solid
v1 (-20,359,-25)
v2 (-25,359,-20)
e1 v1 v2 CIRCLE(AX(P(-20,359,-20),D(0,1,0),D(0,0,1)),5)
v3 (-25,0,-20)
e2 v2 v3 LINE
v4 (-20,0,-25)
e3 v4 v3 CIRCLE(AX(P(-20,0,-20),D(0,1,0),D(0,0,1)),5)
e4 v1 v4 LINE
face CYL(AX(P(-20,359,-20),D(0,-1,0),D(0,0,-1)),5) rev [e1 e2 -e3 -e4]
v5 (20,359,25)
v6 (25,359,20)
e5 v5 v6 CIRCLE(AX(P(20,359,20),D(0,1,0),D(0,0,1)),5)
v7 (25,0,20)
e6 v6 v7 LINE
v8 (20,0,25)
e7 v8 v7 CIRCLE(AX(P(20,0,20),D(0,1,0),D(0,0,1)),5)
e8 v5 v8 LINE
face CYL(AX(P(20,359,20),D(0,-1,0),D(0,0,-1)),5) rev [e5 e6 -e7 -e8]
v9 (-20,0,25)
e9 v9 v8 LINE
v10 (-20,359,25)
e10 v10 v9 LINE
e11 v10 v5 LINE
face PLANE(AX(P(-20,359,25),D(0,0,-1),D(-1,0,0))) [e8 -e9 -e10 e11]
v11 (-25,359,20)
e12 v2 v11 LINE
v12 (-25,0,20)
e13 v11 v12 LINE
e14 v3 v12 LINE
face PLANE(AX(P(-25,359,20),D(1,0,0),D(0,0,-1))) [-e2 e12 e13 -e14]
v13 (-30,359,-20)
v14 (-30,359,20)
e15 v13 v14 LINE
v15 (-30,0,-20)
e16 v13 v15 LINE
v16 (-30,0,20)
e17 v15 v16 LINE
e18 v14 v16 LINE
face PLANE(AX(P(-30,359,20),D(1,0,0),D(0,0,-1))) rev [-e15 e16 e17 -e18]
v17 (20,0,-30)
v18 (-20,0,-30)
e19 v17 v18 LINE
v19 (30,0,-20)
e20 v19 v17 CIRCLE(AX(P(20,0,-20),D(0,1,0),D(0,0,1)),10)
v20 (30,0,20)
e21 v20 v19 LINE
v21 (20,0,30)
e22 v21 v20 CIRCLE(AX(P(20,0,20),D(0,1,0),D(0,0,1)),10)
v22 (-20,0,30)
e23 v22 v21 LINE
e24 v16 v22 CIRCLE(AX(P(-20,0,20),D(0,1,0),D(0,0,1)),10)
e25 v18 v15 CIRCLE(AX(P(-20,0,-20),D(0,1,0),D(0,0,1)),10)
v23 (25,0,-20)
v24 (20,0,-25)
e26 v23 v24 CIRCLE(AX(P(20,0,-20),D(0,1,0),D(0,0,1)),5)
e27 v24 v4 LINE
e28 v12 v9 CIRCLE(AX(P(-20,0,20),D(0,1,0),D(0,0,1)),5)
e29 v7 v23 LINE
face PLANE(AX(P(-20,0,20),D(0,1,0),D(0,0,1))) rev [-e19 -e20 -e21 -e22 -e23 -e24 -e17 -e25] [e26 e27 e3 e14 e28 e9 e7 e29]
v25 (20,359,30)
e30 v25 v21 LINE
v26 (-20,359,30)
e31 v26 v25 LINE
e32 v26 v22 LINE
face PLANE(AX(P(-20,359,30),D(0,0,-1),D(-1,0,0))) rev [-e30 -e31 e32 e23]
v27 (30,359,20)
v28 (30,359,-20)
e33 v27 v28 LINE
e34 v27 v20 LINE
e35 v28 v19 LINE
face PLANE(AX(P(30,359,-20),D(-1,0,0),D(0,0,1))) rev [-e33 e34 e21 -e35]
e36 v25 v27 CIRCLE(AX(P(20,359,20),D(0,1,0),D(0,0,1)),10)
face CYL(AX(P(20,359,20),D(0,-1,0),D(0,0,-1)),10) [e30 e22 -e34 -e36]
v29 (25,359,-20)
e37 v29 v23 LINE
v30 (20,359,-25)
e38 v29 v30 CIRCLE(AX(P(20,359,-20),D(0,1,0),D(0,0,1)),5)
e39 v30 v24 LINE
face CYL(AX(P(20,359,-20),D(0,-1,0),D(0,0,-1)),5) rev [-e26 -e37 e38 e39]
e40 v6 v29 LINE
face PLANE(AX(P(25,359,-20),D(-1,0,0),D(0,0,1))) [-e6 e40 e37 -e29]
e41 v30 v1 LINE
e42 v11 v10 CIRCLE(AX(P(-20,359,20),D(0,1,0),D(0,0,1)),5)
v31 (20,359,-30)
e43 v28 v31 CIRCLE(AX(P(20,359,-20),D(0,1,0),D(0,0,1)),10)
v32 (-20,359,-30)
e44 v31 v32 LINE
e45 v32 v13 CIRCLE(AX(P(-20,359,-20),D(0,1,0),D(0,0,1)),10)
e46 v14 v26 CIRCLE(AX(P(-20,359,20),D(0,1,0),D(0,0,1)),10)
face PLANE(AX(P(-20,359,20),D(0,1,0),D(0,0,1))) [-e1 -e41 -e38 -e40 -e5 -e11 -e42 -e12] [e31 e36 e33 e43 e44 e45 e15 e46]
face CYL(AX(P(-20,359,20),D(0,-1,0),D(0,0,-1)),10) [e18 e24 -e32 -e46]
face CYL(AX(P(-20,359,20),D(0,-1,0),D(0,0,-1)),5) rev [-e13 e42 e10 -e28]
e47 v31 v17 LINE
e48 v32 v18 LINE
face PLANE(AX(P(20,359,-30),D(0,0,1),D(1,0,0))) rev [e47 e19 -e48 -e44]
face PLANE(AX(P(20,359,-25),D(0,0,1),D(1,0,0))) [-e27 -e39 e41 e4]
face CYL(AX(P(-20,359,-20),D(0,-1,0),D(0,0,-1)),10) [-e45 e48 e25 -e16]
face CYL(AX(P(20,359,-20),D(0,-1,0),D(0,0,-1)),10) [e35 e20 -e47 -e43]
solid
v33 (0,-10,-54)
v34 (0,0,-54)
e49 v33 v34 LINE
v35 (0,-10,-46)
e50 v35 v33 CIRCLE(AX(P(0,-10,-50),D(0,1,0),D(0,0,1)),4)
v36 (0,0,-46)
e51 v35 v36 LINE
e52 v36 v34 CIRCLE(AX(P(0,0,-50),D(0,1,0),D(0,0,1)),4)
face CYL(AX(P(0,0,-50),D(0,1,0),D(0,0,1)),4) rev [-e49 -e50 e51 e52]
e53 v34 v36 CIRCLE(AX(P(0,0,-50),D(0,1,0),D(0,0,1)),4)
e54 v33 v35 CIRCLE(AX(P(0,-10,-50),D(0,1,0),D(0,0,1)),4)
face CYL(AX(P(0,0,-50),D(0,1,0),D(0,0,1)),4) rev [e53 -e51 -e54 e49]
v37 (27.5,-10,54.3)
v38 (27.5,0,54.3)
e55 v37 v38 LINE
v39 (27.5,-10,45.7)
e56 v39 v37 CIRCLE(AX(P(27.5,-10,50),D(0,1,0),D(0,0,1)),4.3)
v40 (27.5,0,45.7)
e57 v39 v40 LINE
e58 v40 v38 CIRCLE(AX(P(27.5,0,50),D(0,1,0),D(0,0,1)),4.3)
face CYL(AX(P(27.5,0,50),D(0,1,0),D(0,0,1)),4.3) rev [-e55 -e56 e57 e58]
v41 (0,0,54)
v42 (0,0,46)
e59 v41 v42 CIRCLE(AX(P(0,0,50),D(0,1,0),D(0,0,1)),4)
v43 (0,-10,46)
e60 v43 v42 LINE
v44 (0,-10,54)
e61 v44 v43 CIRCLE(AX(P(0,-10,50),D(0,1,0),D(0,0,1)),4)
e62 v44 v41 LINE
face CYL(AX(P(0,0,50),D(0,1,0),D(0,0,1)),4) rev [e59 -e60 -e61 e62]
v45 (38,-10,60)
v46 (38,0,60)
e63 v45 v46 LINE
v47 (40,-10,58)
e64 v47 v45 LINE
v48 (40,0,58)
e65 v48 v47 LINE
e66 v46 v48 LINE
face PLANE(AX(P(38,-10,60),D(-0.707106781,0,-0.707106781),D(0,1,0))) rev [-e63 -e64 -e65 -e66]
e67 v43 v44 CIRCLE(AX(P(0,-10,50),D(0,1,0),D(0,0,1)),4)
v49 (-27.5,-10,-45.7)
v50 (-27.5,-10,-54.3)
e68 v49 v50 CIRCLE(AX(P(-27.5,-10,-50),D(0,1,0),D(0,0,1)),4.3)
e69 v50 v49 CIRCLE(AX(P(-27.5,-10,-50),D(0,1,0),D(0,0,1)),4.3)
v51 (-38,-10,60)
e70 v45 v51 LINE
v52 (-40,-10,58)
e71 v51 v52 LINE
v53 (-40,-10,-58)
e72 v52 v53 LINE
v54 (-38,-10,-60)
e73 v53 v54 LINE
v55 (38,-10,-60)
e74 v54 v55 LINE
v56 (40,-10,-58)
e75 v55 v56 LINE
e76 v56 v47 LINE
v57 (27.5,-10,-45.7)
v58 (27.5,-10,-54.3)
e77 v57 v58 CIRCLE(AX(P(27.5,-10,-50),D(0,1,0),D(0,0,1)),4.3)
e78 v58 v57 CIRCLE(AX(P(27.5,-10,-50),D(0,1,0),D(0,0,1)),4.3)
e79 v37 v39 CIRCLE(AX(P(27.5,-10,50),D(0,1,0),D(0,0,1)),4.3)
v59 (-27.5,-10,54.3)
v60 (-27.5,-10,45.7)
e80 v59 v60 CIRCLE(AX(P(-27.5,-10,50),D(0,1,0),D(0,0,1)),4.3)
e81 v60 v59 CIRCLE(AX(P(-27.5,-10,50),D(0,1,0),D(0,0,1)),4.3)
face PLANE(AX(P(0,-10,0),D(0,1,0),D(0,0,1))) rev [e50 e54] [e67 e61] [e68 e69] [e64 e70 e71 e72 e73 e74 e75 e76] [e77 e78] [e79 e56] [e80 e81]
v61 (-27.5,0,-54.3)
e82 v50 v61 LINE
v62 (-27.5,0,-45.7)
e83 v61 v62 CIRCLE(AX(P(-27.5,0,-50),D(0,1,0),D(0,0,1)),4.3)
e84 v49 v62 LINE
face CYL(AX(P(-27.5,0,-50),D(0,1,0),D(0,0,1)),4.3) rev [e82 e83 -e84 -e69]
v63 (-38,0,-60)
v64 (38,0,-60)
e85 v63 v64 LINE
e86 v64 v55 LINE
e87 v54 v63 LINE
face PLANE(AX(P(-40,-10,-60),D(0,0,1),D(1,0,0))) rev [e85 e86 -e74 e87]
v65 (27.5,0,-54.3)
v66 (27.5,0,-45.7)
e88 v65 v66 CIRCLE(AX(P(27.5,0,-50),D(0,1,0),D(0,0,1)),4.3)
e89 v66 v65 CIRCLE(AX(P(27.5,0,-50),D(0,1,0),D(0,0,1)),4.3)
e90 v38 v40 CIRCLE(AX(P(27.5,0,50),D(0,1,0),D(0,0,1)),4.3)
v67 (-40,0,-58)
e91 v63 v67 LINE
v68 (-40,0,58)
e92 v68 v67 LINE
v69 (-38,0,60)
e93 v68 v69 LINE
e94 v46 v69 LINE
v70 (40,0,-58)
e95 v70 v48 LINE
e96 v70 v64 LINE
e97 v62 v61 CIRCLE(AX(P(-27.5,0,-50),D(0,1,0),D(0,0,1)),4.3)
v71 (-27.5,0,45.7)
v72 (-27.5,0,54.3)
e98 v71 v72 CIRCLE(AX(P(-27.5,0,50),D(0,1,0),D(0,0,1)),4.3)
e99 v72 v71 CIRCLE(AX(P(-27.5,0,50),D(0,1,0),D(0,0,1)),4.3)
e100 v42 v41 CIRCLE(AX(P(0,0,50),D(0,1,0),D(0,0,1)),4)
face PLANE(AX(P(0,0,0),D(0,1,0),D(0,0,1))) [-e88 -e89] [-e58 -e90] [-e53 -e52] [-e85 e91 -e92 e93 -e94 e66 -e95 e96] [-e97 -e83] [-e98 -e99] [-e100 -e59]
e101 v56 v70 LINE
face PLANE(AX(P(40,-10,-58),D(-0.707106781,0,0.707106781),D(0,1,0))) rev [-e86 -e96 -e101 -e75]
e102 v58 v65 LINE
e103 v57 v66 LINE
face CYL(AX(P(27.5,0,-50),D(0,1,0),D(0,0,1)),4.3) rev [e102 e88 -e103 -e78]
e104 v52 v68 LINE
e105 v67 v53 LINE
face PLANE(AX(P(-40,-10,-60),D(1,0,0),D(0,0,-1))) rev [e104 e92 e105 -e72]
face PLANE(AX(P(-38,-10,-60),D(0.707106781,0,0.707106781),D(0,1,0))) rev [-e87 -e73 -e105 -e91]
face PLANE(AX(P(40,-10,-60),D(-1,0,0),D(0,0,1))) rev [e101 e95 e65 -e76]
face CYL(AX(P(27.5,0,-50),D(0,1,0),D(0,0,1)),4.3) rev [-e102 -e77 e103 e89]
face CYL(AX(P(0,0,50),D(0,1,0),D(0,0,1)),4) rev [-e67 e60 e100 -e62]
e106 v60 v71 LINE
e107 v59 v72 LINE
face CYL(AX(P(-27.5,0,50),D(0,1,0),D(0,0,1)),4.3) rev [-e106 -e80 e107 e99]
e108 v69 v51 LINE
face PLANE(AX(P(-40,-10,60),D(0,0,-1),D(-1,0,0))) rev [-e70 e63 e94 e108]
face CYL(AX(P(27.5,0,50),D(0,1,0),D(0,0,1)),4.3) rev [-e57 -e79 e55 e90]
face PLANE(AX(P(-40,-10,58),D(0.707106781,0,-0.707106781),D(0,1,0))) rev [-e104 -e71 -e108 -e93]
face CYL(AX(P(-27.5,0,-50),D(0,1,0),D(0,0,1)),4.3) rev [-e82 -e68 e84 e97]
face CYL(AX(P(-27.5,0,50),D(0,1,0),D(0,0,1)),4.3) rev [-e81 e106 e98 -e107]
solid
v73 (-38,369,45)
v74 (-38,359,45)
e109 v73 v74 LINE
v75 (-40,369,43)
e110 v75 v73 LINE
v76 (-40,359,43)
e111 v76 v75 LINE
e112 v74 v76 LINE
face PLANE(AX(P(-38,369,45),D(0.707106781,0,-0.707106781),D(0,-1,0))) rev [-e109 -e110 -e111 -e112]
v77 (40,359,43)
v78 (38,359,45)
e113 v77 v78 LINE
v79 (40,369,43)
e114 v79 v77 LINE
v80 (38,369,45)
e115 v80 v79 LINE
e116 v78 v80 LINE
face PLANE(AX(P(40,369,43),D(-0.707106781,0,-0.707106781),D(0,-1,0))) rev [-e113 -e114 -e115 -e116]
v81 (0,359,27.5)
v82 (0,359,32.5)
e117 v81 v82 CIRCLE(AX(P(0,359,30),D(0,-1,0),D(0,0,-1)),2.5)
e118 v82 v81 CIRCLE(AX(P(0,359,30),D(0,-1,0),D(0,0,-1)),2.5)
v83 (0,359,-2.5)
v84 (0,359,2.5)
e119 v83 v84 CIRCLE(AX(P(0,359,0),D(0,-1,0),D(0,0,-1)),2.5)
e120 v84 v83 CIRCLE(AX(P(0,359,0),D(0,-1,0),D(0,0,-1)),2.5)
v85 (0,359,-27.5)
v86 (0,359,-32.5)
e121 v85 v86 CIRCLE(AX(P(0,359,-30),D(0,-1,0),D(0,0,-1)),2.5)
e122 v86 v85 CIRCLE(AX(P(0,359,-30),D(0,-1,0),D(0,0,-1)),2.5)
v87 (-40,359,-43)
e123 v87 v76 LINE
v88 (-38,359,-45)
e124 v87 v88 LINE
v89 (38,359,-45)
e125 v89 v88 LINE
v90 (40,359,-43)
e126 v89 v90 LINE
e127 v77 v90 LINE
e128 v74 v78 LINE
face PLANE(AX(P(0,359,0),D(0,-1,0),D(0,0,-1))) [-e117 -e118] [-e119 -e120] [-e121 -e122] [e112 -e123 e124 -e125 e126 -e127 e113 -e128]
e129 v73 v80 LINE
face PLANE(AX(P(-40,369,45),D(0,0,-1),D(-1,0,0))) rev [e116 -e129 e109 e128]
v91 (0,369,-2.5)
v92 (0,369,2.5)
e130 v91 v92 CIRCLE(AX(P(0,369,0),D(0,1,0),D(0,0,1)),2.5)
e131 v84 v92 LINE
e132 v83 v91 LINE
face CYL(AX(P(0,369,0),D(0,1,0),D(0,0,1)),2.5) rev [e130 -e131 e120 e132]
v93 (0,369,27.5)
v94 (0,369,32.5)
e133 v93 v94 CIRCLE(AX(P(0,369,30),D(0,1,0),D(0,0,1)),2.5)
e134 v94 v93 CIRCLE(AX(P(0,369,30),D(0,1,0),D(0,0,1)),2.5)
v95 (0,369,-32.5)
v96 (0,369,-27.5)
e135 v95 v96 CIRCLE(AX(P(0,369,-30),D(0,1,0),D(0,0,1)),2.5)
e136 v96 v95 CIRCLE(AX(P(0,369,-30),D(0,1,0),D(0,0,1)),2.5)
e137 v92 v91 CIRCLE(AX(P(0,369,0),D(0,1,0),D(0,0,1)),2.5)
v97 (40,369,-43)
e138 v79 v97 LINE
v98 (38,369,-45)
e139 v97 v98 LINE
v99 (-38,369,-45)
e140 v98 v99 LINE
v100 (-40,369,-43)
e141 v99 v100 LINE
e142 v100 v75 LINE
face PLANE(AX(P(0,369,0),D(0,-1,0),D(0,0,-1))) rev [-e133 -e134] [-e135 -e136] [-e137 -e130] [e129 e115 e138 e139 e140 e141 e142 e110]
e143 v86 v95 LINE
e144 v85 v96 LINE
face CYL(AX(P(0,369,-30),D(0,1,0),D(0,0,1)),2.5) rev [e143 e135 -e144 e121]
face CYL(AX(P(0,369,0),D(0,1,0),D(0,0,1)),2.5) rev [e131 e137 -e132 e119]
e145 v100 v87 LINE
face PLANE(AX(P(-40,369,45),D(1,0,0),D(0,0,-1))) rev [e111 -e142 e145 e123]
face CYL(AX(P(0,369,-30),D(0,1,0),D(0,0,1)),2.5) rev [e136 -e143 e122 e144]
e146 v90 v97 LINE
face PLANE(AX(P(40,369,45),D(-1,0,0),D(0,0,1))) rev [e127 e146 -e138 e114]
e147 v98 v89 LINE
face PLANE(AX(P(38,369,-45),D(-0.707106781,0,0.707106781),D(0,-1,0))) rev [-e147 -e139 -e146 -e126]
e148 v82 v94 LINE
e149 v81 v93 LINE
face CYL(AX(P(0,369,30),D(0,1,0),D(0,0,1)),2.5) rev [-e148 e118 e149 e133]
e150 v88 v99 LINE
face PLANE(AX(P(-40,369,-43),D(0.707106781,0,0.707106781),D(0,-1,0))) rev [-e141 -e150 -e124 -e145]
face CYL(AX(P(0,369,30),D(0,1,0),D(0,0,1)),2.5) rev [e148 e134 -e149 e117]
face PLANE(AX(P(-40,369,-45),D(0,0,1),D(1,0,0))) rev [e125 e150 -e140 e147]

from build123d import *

# Parameters (mm, degrees)
MEMBER_1_DEPTH                   = 359
SKETCH_4_W                       = 80
SKETCH_4_H                       = 120
EXTRUDE_1_DEPTH                  = 10
CHAMFER_1_SIZE                   = 2
HOLE_WIZARD_8_6_8_6_1_AT_2_COUNT = 2
HOLE_WIZARD_8_6_8_6_1_AT_2_PITCH = 114.127122105
HOLE_WIZARD_8_6_8_6_1_AT_3_COUNT = 2
HOLE_WIZARD_8_6_8_6_1_AT_3_PITCH = 55
HOLE_WIZARD_8_6_8_6_1_AT_4_COUNT = 2
HOLE_WIZARD_8_6_8_6_1_AT_4_PITCH = 100
HOLE_WIZARD_8_0_8_1_AT_2_COUNT   = 2
HOLE_WIZARD_8_0_8_1_AT_2_PITCH   = 100
SKETCH_13_W                      = 80
SKETCH_13_H                      = 90
EXTRUDE_2_DEPTH                  = 10
CHAMFER_2_SIZE                   = 2
HOLE_WIZARD_M6_1_AT_2_COUNT      = 2
HOLE_WIZARD_M6_1_AT_2_PITCH      = 60


with BuildPart() as part:
    # Sketch1 → Member 1 (new body)
    with BuildSketch(Plane(origin=(0, 0, 0), x_dir=(-1, 0, 0), z_dir=(0, 1, 0))):
        with BuildLine():
            Line((-20, -30), (20, -30))
            ThreePointArc((20, -30), (27.071067812, -27.071067812), (30, -20))
            Line((30, -20), (30, 20))
            ThreePointArc((30, 20), (27.071067812, 27.071067812), (20, 30))
            Line((20, 30), (-20, 30))
            ThreePointArc((-20, 30), (-27.071067812, 27.071067812), (-30, 20))
            Line((-30, 20), (-30, -20))
            ThreePointArc((-30, -20), (-27.071067812, -27.071067812), (-20, -30))
        make_face()
        with BuildLine():
            Line((-20, -25), (20, -25))
            ThreePointArc((20, -25), (23.535533906, -23.535533906), (25, -20))
            Line((25, -20), (25, 20))
            ThreePointArc((25, 20), (23.535533906, 23.535533906), (20, 25))
            Line((20, 25), (-20, 25))
            ThreePointArc((-20, 25), (-23.535533906, 23.535533906), (-25, 20))
            Line((-25, 20), (-25, -20))
            ThreePointArc((-25, -20), (-23.535533906, -23.535533906), (-20, -25))
        make_face(mode=Mode.SUBTRACT)
    extrude(amount=MEMBER_1_DEPTH)


with BuildPart() as body_2:
    # 草图4 → 凸台-拉伸1 (new body)
    with BuildSketch(Plane.XZ):
        Rectangle(SKETCH_4_W, SKETCH_4_H)
    extrude(amount=EXTRUDE_1_DEPTH)

    # 倒角1
    chamfer_1_edges = [body_2.edges().sort_by_distance(p)[0] for p in [
        (40, -5, -60),
        (-40, -5, -60),
        (-40, -5, 60),
        (40, -5, 60),
    ]]
    chamfer(chamfer_1_edges, length=CHAMFER_1_SIZE)

    # 草图5 → Ø8.6 (8.6) 直径孔1 (revolve, cut)
    with BuildSketch(Plane(origin=(27.5, 0, -50), x_dir=(0, 0, 1), z_dir=(1, 0, 0))):
        Polygon((0, 0), (0, 18.092606158), (4.3, 15.61), (4.3, 0), align=None)
    hole_wizard_8_6_8_6_1 = revolve(axis=Axis((27.5, 6.35, -50), (0, -1, 0)), mode=Mode.SUBTRACT)

    # Ø8.6 (8.6) 直径孔1 at 2: Ø8.6 (8.6) 直径孔1 ×2
    with Locations(*[Vector(-0.481918749772156, 0, 0.876215908676647) * (i * HOLE_WIZARD_8_6_8_6_1_AT_2_PITCH) for i in range(1, HOLE_WIZARD_8_6_8_6_1_AT_2_COUNT)]):
        add(hole_wizard_8_6_8_6_1, mode=Mode.SUBTRACT)

    # Ø8.6 (8.6) 直径孔1 at 3: Ø8.6 (8.6) 直径孔1 ×2
    with Locations(*[(-i * HOLE_WIZARD_8_6_8_6_1_AT_3_PITCH, 0, 0) for i in range(1, HOLE_WIZARD_8_6_8_6_1_AT_3_COUNT)]):
        add(hole_wizard_8_6_8_6_1, mode=Mode.SUBTRACT)

    # Ø8.6 (8.6) 直径孔1 at 4: Ø8.6 (8.6) 直径孔1 ×2
    with Locations(*[(0, 0, i * HOLE_WIZARD_8_6_8_6_1_AT_4_PITCH) for i in range(1, HOLE_WIZARD_8_6_8_6_1_AT_4_COUNT)]):
        add(hole_wizard_8_6_8_6_1, mode=Mode.SUBTRACT)

    # 草图11 → Ø8.0 (8) 直径孔1 (revolve, cut)
    with BuildSketch(Plane(origin=(0, 0, -50), x_dir=(0, 0, 1), z_dir=(1, 0, 0))):
        Polygon((0, 0), (0, 17.919401077), (4, 15.61), (4, 0), align=None)
    hole_wizard_8_0_8_1 = revolve(axis=Axis((0, 6.35, -50), (0, -1, 0)), mode=Mode.SUBTRACT)

    # Ø8.0 (8) 直径孔1 at 2: Ø8.0 (8) 直径孔1 ×2
    with Locations(*[(0, 0, i * HOLE_WIZARD_8_0_8_1_AT_2_PITCH) for i in range(1, HOLE_WIZARD_8_0_8_1_AT_2_COUNT)]):
        add(hole_wizard_8_0_8_1, mode=Mode.SUBTRACT)


with BuildPart() as body_3:
    # 草图13 → 凸台-拉伸2 (new body)
    with BuildSketch(Plane(origin=(0, 359, 0), x_dir=(1, 0, 0), z_dir=(0, 1, 0))):
        Rectangle(SKETCH_13_W, SKETCH_13_H)
    extrude(amount=EXTRUDE_2_DEPTH)

    # 倒角2
    chamfer_2_edges = [body_3.edges().sort_by_distance(p)[0] for p in [
        (40, 364, 45),
        (-40, 364, 45),
        (-40, 364, -45),
        (40, 364, -45),
    ]]
    chamfer(chamfer_2_edges, length=CHAMFER_2_SIZE)

    # 草图15 → Ø5.0 (5) 直径孔1 (revolve, cut)
    with BuildSketch(Plane(origin=(0, 369, 0), x_dir=(0, 0, 1), z_dir=(1, 0, 0))):
        Polygon((0, 0), (0, 17.053375673), (2.5, 15.61), (2.5, 0), align=None)
    revolve(axis=Axis((0, 375.35, 0), (0, -1, 0)), mode=Mode.SUBTRACT)

    # 草图17 → M6 螺纹孔1 (revolve, cut)
    with BuildSketch(Plane(origin=(0, 369, -30), x_dir=(0, 0, 1), z_dir=(1, 0, 0))):
        Polygon((0, 0), (0, 18.502151548), (2.5, 17), (2.5, 0), align=None)
    hole_wizard_m6_1 = revolve(axis=Axis((0, 375.35, -30), (0, -1, 0)), mode=Mode.SUBTRACT)

    # M6 螺纹孔1 at 2: M6 螺纹孔1 ×2
    with Locations(*[(0, 0, i * HOLE_WIZARD_M6_1_AT_2_PITCH) for i in range(1, HOLE_WIZARD_M6_1_AT_2_COUNT)]):
        add(hole_wizard_m6_1, mode=Mode.SUBTRACT)


solid = Compound([part.part, body_2.part, body_3.part])
